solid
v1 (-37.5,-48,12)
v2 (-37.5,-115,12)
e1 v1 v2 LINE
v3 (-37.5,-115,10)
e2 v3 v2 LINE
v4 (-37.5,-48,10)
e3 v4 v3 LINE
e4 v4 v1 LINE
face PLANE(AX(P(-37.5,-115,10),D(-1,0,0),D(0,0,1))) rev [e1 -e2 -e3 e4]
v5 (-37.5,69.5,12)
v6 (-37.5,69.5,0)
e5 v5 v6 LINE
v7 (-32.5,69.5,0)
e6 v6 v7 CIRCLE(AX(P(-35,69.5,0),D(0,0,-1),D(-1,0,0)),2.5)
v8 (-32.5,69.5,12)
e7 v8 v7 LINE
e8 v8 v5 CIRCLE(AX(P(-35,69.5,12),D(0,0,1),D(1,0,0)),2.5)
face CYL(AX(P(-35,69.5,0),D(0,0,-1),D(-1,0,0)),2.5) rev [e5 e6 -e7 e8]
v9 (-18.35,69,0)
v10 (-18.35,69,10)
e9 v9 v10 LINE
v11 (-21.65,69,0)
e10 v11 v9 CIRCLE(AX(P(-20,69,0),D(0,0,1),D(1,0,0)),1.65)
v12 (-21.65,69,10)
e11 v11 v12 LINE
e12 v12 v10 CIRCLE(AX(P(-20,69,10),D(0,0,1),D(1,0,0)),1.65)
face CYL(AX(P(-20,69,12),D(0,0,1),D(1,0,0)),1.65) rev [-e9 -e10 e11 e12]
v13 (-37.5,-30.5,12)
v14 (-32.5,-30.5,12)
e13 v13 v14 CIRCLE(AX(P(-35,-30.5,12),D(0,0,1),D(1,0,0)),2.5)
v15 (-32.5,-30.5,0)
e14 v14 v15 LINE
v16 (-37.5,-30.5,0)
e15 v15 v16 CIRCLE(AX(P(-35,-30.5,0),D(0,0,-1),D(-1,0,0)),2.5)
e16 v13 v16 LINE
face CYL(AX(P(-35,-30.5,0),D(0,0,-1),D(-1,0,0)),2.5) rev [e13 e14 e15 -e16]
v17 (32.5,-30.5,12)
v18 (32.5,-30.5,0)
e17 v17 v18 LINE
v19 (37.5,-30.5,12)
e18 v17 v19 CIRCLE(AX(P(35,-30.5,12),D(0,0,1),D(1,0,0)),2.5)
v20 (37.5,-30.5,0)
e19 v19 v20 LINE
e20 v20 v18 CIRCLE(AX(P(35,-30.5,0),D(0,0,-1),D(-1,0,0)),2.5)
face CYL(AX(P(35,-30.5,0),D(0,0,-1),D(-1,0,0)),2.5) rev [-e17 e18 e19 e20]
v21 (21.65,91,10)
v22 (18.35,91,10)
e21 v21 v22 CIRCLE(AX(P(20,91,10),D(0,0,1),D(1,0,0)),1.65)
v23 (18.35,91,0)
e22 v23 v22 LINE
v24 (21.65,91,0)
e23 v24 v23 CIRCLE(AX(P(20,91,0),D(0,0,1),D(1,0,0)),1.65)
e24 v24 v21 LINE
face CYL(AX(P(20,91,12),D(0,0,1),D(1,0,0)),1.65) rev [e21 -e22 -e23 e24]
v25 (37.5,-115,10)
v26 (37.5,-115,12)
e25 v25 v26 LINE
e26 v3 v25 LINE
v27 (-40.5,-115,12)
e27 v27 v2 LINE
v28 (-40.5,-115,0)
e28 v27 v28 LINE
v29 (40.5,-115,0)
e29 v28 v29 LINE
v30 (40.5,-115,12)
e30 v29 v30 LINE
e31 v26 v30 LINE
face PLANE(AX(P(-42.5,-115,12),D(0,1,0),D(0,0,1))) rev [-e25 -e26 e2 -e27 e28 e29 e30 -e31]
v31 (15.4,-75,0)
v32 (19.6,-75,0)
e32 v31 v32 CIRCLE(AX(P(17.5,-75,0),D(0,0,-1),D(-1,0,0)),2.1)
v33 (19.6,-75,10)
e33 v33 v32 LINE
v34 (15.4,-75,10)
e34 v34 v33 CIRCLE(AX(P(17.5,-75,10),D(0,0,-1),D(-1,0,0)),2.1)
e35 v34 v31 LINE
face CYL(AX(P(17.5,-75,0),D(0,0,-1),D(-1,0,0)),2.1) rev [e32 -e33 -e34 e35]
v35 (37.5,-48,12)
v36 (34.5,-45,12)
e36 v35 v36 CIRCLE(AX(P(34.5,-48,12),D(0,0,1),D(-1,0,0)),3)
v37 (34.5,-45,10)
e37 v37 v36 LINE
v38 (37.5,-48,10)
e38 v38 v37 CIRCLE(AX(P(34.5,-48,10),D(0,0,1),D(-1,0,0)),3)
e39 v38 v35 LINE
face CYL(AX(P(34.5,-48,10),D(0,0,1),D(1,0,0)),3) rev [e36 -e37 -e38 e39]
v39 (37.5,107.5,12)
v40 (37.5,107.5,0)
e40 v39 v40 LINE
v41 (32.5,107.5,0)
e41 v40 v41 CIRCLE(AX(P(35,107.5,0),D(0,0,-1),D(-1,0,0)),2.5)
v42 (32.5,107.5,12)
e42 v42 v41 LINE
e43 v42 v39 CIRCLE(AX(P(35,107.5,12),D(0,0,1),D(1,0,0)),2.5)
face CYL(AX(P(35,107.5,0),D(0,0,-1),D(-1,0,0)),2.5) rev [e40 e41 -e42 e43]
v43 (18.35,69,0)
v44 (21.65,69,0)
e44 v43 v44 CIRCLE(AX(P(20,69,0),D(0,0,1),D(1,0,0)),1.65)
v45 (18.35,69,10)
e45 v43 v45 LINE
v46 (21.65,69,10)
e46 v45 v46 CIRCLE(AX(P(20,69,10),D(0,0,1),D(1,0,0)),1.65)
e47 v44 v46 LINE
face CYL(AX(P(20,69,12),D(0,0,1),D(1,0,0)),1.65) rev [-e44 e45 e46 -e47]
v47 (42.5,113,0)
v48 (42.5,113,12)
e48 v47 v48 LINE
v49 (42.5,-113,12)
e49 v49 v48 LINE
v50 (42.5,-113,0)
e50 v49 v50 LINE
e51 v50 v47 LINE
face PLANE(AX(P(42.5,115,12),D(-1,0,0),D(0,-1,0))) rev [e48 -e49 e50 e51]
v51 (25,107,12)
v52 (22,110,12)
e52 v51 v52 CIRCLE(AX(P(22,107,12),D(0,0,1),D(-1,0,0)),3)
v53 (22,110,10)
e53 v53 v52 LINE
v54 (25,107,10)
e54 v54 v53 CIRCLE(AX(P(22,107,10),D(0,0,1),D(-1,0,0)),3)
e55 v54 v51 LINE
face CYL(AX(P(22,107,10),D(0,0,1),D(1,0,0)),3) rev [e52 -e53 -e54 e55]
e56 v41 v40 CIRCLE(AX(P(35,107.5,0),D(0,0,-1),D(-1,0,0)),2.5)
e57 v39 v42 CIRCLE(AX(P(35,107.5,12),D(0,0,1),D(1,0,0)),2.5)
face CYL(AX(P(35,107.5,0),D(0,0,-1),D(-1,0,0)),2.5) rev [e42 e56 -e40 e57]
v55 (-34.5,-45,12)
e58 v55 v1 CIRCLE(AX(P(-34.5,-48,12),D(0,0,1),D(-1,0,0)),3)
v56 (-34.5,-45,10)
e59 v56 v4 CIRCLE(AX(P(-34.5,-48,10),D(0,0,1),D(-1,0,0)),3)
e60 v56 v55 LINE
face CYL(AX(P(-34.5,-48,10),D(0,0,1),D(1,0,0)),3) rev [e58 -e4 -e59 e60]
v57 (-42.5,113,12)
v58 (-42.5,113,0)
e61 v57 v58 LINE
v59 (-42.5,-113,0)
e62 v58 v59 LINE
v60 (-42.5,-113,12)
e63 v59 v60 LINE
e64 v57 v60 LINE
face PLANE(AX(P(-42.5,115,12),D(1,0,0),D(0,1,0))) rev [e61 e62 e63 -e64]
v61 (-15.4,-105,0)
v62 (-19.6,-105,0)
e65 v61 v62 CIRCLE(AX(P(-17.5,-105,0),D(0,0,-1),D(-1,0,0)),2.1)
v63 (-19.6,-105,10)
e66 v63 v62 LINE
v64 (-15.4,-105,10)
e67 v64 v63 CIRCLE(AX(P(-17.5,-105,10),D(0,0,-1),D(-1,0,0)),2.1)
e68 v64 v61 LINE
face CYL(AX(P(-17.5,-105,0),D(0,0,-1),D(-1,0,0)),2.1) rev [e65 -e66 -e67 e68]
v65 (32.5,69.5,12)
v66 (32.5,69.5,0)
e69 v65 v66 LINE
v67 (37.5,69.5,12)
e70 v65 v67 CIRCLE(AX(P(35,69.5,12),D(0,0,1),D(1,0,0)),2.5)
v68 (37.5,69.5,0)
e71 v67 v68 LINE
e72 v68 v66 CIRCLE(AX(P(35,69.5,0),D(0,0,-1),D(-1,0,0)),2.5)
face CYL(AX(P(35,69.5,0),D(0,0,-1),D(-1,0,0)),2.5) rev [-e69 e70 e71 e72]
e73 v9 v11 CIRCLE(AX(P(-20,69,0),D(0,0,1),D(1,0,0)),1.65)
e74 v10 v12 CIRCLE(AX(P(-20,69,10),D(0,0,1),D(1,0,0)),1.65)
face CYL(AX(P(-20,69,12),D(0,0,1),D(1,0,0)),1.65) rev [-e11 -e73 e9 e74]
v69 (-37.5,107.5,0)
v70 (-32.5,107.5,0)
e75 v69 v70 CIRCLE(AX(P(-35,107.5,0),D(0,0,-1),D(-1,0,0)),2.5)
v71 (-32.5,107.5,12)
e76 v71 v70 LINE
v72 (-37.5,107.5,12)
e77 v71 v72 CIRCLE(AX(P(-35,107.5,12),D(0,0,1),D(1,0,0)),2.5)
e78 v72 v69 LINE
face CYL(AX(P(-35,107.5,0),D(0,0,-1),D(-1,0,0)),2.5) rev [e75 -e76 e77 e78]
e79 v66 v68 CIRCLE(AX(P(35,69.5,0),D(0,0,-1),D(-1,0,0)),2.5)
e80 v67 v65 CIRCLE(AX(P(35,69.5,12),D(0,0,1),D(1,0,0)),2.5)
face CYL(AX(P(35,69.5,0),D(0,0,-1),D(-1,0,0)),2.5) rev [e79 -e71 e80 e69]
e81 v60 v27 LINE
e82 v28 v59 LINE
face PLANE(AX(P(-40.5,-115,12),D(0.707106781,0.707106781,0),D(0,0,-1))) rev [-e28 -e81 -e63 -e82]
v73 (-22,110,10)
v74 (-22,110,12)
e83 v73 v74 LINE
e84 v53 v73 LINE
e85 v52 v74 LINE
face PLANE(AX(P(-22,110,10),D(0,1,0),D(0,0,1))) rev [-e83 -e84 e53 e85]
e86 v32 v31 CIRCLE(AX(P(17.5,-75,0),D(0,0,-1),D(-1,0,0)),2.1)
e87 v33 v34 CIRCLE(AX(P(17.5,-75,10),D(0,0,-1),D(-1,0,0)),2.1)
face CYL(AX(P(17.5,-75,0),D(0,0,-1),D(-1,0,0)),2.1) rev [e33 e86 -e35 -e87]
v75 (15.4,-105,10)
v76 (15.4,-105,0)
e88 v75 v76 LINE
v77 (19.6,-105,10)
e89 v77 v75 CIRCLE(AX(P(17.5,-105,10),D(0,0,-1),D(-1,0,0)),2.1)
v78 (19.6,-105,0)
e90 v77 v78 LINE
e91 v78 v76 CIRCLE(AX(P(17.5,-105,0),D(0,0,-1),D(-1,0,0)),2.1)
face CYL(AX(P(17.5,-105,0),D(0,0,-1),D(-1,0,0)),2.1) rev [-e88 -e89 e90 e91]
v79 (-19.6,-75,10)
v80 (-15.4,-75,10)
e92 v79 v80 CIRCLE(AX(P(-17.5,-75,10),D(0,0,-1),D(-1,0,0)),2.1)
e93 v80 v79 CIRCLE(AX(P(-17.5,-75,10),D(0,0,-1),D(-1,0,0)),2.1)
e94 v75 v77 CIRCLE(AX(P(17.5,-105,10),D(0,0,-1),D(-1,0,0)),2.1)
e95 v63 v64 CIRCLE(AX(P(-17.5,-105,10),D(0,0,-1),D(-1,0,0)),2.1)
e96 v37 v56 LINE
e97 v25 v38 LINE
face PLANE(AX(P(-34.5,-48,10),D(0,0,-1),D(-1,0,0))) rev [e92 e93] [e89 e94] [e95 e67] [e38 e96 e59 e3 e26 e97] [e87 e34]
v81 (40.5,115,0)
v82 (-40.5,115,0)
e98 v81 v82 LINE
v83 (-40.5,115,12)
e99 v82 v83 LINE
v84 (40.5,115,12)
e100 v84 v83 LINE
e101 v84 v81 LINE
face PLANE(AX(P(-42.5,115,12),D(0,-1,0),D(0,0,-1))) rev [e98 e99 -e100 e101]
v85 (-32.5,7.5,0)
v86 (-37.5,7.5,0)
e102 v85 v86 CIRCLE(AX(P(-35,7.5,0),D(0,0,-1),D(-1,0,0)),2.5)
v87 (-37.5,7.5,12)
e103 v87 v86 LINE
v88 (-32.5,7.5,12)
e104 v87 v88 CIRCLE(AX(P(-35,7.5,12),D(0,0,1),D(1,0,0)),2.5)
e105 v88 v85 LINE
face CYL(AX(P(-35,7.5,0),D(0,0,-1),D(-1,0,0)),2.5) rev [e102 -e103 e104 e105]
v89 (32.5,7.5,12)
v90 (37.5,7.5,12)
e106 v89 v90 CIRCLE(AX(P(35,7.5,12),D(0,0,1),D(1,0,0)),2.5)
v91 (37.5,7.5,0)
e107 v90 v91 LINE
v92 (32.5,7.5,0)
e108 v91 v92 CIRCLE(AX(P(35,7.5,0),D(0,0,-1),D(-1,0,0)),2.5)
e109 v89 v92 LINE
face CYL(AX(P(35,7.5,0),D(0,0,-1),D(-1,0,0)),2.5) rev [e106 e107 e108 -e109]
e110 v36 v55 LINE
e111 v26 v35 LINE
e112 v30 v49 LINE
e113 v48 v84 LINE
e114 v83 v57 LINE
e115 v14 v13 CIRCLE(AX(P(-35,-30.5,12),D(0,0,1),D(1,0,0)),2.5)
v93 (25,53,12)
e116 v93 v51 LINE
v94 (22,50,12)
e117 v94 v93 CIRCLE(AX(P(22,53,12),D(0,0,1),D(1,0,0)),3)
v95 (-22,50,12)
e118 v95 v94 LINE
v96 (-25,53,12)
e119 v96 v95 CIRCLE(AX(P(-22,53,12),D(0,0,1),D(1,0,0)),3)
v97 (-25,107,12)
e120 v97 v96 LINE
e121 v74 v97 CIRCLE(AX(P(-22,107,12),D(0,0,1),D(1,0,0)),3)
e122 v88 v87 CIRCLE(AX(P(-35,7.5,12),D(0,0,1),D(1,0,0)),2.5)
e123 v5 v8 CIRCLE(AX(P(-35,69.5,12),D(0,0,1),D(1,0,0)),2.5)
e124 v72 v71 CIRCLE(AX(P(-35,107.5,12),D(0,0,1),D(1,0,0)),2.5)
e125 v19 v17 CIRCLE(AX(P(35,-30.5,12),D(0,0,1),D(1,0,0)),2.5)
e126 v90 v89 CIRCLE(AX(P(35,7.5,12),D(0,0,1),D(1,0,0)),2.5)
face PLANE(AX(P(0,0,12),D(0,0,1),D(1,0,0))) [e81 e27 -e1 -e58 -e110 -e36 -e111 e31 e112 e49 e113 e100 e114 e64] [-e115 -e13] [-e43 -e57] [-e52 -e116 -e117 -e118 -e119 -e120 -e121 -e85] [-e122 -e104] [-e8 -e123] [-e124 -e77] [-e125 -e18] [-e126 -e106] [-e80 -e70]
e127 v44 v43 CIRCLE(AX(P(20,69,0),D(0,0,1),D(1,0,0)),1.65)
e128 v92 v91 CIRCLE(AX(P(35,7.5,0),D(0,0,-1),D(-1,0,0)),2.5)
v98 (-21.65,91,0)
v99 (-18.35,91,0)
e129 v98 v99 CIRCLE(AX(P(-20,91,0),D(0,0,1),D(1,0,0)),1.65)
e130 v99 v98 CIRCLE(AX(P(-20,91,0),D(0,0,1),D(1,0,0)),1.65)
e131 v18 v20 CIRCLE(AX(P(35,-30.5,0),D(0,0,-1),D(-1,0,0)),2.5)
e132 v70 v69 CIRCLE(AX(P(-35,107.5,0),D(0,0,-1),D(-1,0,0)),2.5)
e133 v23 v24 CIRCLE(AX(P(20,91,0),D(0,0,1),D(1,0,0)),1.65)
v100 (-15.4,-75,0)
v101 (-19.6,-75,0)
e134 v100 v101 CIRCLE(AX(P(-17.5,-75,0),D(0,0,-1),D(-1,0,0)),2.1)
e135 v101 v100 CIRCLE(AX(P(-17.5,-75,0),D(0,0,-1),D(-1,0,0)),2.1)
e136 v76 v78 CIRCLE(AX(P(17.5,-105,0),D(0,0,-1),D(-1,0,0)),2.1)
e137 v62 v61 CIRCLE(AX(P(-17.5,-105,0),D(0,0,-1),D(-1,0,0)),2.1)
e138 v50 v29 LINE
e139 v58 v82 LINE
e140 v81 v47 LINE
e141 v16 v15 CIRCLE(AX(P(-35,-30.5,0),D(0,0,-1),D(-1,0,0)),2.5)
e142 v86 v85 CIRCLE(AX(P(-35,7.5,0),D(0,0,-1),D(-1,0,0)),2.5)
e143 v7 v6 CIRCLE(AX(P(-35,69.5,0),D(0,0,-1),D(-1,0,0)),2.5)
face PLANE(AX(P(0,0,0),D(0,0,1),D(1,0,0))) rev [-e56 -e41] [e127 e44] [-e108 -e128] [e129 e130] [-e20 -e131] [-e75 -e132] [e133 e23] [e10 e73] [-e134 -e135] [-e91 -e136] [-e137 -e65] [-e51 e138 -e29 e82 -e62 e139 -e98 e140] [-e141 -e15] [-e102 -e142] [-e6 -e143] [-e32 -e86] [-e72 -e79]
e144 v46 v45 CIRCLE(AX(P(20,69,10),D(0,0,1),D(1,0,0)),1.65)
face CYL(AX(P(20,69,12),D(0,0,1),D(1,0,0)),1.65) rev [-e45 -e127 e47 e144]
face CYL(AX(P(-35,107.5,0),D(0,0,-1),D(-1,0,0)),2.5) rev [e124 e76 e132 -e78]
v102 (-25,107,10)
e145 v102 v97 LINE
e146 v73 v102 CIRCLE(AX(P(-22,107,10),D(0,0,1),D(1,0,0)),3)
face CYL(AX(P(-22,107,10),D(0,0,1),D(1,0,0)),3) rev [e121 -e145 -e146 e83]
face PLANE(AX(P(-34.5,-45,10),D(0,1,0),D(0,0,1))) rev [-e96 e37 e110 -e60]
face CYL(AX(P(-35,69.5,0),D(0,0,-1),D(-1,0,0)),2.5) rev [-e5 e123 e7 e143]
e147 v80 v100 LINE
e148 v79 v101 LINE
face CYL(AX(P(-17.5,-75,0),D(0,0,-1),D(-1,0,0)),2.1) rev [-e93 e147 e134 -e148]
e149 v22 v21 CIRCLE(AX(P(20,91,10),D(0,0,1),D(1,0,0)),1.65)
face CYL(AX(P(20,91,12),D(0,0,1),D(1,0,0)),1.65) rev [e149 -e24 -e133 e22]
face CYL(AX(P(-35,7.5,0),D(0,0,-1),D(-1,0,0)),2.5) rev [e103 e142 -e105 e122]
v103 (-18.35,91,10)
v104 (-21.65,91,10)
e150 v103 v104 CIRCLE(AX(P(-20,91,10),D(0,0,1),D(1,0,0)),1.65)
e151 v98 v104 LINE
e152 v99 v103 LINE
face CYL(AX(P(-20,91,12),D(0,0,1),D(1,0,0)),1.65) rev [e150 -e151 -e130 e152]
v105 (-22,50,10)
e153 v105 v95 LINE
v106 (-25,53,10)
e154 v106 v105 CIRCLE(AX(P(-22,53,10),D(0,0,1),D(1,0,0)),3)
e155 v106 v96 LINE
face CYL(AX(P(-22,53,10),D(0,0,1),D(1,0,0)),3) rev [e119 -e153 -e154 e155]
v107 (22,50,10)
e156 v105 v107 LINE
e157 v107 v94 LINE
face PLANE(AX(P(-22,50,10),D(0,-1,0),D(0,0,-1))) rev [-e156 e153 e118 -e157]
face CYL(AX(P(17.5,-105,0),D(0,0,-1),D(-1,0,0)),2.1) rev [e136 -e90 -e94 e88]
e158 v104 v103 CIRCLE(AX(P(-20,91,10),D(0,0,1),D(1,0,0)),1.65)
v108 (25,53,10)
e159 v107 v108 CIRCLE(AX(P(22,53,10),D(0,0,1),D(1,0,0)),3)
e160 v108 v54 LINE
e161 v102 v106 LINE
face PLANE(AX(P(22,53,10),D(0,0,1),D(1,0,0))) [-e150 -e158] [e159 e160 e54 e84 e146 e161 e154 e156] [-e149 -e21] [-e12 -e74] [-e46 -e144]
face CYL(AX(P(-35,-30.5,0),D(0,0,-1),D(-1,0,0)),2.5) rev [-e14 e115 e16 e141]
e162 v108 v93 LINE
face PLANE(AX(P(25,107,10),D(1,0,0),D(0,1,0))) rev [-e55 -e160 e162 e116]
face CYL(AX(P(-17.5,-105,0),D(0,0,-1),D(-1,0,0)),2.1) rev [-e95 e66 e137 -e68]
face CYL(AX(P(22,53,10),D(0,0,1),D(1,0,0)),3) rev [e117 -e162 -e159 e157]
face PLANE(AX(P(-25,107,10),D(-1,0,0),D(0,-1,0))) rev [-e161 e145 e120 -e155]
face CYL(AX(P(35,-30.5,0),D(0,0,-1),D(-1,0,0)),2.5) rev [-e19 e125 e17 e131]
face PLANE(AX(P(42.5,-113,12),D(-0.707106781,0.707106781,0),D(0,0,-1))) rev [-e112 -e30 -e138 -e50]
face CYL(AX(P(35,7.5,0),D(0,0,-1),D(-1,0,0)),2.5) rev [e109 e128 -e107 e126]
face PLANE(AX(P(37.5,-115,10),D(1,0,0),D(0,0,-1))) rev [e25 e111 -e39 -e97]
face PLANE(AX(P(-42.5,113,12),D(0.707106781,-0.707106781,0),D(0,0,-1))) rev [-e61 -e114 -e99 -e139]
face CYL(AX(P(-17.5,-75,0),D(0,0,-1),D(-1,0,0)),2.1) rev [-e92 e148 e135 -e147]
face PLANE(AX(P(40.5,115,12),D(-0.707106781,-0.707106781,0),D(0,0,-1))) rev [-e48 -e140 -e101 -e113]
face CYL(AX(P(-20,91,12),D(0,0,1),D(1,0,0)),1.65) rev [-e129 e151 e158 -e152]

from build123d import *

# Parameters (mm, degrees)
SKETCH_2_W             = 85
SKETCH_2_H             = 230
EXTRUDE_1_DEPTH        = 12
CUT_EXTRUDE_2_DEPTH    = 2
HOLE_WIZARD_M5_1_D     = 4.2
HOLE_WIZARD_M4_1_D     = 3.3
HOLE_WIZARD_M6_1_D     = 5
HOLE_WIZARD_M6_1_DEPTH = 15
HOLE_WIZARD_M6_1_TIP   = 1.502151548
CHAMFER_1_SIZE         = 2


with BuildPart() as part:
    # 草图2 → 凸台-拉伸1 (new body)
    with BuildSketch(Plane.XY):
        Rectangle(SKETCH_2_W, SKETCH_2_H)
    extrude(amount=EXTRUDE_1_DEPTH)

    # 草图16 → 切除-拉伸2 (cut)
    with BuildSketch(Plane.XY.offset(12)):
        with BuildLine():
            Line((-22, 110), (22, 110))
            ThreePointArc((22, 110), (24.121320344, 109.121320344), (25, 107))
            Line((25, 107), (25, 53))
            ThreePointArc((25, 53), (24.121320344, 50.878679656), (22, 50))
            Line((22, 50), (-22, 50))
            ThreePointArc((-22, 50), (-24.121320344, 50.878679656), (-25, 53))
            Line((-25, 53), (-25, 107))
            ThreePointArc((-25, 107), (-24.121320344, 109.121320344), (-22, 110))
        make_face()
        with BuildLine():
            Line((-37.5, -115), (37.5, -115))
            Line((37.5, -115), (37.5, -48))
            ThreePointArc((37.5, -48), (36.621320344, -45.878679656), (34.5, -45))
            Line((34.5, -45), (-34.5, -45))
            ThreePointArc((-34.5, -45), (-36.621320344, -45.878679656), (-37.5, -48))
            Line((-37.5, -48), (-37.5, -115))
        make_face()
    extrude(amount=-CUT_EXTRUDE_2_DEPTH, mode=Mode.SUBTRACT)

    # M5 螺纹孔1 (through all)
    with Locations(Plane(origin=(0, 0, 0), x_dir=(-1, 0, 0), z_dir=(0, 0, -1))):
        with Locations((-17.5, -75), (17.5, -75), (17.5, -105), (-17.5, -105)):
            Hole(HOLE_WIZARD_M5_1_D / 2)

    # M4 螺纹孔1 (through all)
    with Locations(Plane.XY.offset(12)):
        with Locations((-20, 69), (20, 69), (-20, 91), (20, 91)):
            Hole(HOLE_WIZARD_M4_1_D / 2)

    # M6 螺纹孔1
    with Locations(Plane(origin=(0, 0, 0), x_dir=(-1, 0, 0), z_dir=(0, 0, -1))):
        with Locations((-35, 107.5), (-35, 69.5), (35, 69.5), (35, 107.5), (-35, 7.5), (-35, -30.5), (35, -30.5), (35, 7.5)):
            Hole(HOLE_WIZARD_M6_1_D / 2, depth=HOLE_WIZARD_M6_1_DEPTH)
            with Locations((0, 0, -(HOLE_WIZARD_M6_1_DEPTH + HOLE_WIZARD_M6_1_TIP / 2))):  # 118° drill point
                Cone(0, HOLE_WIZARD_M6_1_D / 2, HOLE_WIZARD_M6_1_TIP, mode=Mode.SUBTRACT)

    # 倒角1
    chamfer_1_edges = [part.edges().sort_by_distance(p)[0] for p in [
        (42.5, -115, 6),
        (-42.5, -115, 6),
        (-42.5, 115, 6),
        (42.5, 115, 6),
    ]]
    chamfer(chamfer_1_edges, length=CHAMFER_1_SIZE)


solid = part.part
